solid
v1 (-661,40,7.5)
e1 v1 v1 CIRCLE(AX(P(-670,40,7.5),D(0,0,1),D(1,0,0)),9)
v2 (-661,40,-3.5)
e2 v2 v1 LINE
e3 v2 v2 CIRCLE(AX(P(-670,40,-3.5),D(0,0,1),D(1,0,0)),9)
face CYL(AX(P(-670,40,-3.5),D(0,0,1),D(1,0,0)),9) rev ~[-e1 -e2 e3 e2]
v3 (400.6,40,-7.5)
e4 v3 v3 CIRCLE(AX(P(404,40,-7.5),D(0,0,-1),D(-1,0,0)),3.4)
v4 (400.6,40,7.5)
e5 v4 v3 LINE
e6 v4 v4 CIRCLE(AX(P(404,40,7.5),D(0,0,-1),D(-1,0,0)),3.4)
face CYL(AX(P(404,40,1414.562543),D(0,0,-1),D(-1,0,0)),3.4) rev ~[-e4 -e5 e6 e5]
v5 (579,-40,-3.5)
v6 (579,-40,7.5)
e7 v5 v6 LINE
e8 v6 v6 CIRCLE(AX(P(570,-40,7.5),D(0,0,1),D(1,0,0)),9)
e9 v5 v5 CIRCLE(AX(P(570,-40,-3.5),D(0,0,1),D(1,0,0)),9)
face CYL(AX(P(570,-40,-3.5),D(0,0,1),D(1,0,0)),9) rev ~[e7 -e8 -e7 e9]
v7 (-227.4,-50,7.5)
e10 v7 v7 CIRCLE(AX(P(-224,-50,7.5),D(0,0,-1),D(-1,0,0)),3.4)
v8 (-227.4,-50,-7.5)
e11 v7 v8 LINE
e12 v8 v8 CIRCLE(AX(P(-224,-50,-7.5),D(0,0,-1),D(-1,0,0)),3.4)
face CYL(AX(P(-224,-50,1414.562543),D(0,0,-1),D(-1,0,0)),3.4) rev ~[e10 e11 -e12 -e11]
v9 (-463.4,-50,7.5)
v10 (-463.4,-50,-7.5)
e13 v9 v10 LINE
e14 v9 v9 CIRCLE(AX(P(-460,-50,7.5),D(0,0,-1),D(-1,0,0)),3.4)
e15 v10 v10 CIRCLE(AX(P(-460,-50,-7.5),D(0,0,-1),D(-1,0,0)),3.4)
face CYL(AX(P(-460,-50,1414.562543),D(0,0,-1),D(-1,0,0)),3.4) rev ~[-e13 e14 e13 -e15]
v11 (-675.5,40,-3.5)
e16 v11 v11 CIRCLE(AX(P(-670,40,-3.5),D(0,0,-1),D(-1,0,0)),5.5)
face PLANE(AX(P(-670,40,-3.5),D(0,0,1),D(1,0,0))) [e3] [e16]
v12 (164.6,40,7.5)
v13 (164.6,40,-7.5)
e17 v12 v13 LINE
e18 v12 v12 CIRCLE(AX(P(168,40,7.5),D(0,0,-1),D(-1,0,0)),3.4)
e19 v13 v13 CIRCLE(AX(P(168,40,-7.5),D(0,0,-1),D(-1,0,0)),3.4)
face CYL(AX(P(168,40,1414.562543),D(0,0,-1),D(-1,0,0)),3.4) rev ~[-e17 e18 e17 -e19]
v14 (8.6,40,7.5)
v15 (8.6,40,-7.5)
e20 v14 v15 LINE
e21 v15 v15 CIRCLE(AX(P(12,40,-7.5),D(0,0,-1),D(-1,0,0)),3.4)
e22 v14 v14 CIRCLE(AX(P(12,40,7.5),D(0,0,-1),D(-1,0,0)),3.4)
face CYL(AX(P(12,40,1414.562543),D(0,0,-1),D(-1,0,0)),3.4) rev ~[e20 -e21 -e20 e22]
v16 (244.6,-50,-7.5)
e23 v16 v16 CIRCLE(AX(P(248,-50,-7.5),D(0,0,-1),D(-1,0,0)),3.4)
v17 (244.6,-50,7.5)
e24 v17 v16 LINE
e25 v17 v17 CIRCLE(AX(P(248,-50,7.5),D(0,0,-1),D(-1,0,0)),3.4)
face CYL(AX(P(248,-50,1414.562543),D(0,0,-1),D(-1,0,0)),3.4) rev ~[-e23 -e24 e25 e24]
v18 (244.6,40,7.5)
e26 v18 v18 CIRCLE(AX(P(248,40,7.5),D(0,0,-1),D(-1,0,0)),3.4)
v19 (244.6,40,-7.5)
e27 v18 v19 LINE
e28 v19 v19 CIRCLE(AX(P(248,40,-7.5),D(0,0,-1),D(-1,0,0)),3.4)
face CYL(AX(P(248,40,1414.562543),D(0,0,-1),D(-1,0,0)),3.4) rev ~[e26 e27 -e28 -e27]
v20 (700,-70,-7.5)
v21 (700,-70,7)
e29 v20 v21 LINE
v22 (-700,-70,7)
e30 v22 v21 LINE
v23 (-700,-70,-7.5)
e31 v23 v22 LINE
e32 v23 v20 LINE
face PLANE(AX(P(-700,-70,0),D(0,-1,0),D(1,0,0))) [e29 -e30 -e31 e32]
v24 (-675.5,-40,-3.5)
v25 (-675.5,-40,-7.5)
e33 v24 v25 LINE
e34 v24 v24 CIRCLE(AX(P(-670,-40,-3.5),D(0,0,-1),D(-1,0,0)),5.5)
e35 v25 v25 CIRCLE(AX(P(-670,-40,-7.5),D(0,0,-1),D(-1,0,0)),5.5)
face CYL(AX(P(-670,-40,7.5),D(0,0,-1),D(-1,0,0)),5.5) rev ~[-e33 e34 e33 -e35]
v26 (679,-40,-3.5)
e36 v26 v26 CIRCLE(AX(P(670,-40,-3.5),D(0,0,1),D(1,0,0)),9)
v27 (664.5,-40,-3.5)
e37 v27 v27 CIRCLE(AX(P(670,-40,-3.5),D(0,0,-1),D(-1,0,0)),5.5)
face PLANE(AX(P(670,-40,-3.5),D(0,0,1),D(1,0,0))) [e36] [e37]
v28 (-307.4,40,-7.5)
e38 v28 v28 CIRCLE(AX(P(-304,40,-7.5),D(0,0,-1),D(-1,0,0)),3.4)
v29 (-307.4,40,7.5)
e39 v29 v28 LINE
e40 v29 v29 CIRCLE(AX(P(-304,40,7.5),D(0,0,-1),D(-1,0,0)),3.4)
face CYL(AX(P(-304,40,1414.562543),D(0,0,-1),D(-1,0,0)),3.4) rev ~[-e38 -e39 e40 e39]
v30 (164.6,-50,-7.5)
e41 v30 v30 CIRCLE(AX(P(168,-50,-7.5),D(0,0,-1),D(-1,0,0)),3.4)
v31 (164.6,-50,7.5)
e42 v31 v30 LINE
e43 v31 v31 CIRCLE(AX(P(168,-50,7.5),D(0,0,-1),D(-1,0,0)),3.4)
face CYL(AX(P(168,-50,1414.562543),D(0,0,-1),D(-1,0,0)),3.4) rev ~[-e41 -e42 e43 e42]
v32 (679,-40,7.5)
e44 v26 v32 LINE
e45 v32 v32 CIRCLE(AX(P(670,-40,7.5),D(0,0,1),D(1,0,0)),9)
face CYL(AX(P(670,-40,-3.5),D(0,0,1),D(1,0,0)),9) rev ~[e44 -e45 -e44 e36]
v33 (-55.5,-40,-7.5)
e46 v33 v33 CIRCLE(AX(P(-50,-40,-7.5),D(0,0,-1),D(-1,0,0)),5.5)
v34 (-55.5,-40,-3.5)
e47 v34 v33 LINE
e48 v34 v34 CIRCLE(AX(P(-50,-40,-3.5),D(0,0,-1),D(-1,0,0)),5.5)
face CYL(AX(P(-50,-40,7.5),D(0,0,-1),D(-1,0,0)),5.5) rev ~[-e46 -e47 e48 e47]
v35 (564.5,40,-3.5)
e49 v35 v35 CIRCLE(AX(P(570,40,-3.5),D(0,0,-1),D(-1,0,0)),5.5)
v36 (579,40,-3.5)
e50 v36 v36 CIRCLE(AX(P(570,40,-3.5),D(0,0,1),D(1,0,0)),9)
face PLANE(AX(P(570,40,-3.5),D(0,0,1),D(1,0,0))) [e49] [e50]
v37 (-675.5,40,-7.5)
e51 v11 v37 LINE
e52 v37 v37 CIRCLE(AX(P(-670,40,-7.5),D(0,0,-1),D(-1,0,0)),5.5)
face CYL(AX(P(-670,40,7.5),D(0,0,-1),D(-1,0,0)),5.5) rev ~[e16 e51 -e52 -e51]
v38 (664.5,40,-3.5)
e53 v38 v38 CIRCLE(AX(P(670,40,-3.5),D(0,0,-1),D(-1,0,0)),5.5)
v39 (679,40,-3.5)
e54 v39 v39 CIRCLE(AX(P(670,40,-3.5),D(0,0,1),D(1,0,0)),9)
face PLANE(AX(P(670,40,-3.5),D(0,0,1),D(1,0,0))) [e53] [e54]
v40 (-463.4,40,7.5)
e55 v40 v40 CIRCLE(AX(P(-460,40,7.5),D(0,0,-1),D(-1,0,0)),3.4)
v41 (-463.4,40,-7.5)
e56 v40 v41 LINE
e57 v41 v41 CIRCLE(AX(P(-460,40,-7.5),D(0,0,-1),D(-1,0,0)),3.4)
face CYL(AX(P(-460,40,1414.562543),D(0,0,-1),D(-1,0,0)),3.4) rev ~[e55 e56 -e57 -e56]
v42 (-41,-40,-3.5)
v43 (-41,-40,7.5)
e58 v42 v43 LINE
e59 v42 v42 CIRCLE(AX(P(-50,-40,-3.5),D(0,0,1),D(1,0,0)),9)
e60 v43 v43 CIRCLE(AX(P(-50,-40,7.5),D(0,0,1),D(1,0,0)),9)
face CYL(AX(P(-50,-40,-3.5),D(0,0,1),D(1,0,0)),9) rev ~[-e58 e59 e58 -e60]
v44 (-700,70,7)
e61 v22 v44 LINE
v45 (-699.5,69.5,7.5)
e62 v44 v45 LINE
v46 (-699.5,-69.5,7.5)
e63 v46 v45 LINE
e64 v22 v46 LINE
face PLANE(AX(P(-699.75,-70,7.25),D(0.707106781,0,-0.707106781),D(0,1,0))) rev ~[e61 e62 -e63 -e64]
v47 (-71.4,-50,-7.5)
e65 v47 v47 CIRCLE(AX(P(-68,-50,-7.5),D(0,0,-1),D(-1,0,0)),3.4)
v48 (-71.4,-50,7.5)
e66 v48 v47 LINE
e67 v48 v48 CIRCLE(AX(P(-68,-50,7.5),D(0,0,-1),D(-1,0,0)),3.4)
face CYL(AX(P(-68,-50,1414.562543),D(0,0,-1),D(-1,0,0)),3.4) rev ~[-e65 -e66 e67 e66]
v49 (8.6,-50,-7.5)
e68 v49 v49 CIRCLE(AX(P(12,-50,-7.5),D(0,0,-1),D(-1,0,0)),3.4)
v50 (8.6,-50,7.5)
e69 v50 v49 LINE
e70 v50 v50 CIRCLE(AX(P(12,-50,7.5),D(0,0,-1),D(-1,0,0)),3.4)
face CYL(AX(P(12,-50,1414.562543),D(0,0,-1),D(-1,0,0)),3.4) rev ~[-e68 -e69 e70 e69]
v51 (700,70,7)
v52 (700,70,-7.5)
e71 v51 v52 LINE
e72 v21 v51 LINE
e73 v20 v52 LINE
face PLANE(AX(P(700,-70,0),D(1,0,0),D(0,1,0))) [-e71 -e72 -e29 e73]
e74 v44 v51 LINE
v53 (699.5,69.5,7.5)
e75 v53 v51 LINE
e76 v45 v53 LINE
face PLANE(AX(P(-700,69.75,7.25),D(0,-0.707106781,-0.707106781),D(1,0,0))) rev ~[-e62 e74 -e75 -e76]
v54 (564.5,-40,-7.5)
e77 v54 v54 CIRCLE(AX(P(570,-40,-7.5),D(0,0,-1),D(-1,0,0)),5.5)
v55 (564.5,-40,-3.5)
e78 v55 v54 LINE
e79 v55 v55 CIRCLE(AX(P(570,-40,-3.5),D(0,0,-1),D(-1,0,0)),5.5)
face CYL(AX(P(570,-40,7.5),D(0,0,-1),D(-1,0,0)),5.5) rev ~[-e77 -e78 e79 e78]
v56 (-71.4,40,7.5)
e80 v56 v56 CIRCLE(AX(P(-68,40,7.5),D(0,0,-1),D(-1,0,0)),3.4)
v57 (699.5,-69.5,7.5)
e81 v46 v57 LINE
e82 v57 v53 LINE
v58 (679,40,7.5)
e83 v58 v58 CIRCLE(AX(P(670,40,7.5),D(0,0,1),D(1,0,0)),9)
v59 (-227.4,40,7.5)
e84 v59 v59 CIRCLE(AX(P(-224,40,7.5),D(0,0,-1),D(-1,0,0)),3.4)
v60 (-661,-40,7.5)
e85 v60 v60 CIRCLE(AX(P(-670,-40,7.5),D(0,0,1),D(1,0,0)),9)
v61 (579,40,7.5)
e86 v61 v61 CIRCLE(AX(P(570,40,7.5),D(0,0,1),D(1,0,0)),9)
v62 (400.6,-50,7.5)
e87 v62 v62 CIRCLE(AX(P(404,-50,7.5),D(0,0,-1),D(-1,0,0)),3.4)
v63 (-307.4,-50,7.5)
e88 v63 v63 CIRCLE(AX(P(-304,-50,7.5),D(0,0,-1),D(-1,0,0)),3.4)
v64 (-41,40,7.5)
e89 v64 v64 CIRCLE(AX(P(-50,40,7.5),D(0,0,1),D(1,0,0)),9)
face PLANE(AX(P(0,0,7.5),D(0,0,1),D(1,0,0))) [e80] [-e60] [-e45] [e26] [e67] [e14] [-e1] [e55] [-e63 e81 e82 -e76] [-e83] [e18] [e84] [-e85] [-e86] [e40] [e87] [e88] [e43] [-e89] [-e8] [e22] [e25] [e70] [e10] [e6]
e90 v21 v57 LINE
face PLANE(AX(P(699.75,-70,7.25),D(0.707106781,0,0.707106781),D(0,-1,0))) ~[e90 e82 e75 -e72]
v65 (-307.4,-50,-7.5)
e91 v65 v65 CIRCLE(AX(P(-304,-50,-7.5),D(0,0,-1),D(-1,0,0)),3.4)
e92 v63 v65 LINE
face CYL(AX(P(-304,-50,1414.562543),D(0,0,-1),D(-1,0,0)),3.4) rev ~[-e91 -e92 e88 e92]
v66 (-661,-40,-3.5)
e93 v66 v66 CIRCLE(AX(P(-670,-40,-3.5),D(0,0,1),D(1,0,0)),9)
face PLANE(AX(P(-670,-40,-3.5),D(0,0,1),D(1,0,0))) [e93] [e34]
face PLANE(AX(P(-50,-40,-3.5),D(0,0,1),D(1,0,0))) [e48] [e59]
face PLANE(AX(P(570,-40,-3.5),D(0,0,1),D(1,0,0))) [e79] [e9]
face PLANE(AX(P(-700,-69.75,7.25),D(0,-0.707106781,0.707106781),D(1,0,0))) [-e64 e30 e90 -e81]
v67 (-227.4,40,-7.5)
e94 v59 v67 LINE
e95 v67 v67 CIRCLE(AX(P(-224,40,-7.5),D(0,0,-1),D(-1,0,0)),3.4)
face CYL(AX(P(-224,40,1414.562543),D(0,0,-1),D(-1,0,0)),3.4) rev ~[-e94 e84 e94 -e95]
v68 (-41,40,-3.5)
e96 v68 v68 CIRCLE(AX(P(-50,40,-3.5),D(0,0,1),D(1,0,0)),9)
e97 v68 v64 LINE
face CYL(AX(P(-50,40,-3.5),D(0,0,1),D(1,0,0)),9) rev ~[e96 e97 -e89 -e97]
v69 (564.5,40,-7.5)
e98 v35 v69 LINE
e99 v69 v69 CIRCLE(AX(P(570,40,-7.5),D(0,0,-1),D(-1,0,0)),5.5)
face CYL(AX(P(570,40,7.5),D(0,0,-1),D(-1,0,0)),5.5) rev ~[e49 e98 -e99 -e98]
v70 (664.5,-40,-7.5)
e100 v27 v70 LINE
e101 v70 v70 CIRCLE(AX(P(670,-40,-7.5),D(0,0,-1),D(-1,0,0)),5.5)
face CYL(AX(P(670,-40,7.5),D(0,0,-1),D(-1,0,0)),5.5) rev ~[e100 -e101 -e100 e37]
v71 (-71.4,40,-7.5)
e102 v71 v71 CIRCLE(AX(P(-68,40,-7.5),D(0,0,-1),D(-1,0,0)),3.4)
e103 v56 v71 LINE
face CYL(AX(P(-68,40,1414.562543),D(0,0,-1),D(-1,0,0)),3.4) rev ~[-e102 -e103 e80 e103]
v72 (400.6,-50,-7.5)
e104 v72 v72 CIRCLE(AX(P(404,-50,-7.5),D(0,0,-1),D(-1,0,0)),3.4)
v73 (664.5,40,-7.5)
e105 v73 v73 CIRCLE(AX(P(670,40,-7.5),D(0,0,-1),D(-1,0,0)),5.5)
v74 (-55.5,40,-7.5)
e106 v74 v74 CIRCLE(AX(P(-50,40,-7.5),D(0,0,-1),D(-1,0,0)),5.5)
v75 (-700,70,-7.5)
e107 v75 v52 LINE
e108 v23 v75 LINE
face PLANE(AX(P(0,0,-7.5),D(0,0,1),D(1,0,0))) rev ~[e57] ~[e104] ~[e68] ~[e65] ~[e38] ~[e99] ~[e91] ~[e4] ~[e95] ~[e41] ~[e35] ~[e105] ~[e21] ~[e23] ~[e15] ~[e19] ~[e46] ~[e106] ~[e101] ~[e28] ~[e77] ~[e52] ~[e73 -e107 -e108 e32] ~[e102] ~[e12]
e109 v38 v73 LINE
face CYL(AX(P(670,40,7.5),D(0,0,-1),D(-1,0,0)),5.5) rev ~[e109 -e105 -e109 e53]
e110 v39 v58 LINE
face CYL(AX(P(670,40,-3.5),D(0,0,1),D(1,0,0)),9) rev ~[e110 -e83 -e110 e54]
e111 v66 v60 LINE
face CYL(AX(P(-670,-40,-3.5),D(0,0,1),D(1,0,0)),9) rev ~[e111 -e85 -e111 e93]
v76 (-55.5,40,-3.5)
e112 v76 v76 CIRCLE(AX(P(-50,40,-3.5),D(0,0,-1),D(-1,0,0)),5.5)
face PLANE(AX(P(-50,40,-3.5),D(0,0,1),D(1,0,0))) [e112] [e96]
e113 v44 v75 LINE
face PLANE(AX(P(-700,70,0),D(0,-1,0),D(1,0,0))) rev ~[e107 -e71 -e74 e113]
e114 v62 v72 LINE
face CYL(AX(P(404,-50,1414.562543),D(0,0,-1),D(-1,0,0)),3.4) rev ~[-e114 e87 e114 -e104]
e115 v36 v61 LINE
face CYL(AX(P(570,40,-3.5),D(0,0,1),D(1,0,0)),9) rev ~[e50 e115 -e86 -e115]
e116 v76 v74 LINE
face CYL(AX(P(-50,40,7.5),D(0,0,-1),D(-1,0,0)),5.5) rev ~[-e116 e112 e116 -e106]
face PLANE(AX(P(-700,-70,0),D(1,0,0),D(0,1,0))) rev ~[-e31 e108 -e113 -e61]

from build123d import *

# Parameters (mm, degrees)
SKETCH_1_W                  = 1400
SKETCH_1_H                  = 140
EXTRUDE_1_DEPTH             = 7.5
HOLE_WIZARD_1_D             = 11
HOLE_WIZARD_1_CBORE_D       = 18
HOLE_WIZARD_1_CBORE_DEPTH   = 11
PATTERN_LINEAR_1_COUNT      = 3
PATTERN_LINEAR_1_PITCH      = 620
PATTERN_LINEAR_1_COUNT_DIR2 = 2
PATTERN_LINEAR_1_PITCH_DIR2 = 80
HOLE_WIZARD_2_D             = 11
HOLE_WIZARD_2_CBORE_D       = 18
HOLE_WIZARD_2_CBORE_DEPTH   = 11
CHAMFER_1_SIZE              = 0.5
HOLE_WIZARD_M8_1_D          = 6.8


with BuildPart() as part:
    # 草图1 → 凸台-拉伸1 (new, symmetric)
    with BuildSketch(Plane.XY):
        Rectangle(SKETCH_1_W, SKETCH_1_H)
    extrude(amount=EXTRUDE_1_DEPTH, both=True)

    # 打孔尺寸(%根据)内六角圆柱头螺钉的类型1 (through all)
    with Locations(Plane(origin=(-670, 40, 7.5), x_dir=(1, 0, 0), z_dir=(0, 0, 1))):
        with Locations((0, 0)):
            hole_wizard_1 = CounterBoreHole(HOLE_WIZARD_1_D / 2, HOLE_WIZARD_1_CBORE_D / 2, HOLE_WIZARD_1_CBORE_DEPTH)

    # 阵列(线性)1: Hole Wizard 1 3 × 2
    with Locations(*[(i * PATTERN_LINEAR_1_PITCH, -j * PATTERN_LINEAR_1_PITCH_DIR2, 0) for i in range(PATTERN_LINEAR_1_COUNT) for j in range(PATTERN_LINEAR_1_COUNT_DIR2) if (i, j) != (0, 0)]):
        add(hole_wizard_1, mode=Mode.SUBTRACT)

    # 打孔尺寸(%根据)内六角圆柱头螺钉的类型2 (through all)
    with Locations(Plane(origin=(670, 40, 7.5), x_dir=(1, 0, 0), z_dir=(0, 0, 1))):
        with Locations((0, 0), (0, -80)):
            CounterBoreHole(HOLE_WIZARD_2_D / 2, HOLE_WIZARD_2_CBORE_D / 2, HOLE_WIZARD_2_CBORE_DEPTH)

    # 倒角1
    chamfer_1_edges = [part.edges().sort_by_distance(p)[0] for p in [
        (-700, 0, 7.5),
        (0, -70, 7.5),
        (700, 0, 7.5),
        (0, 70, 7.5),
    ]]
    chamfer(chamfer_1_edges, length=CHAMFER_1_SIZE)

    # M8 螺纹孔1 (through all)
    with Locations(Plane.XY.offset(7.5)):
        with Locations((-460, 40), (-460, -50), (-304, -50), (-304, 40), (-224, 40), (-224, -50), (-68, -50), (-68, 40), (12, 40), (12, -50), (168, -50), (168, 40), (248, 40), (248, -50), (404, -50), (404, 40)):
            Hole(HOLE_WIZARD_M8_1_D / 2)


solid = part.part
